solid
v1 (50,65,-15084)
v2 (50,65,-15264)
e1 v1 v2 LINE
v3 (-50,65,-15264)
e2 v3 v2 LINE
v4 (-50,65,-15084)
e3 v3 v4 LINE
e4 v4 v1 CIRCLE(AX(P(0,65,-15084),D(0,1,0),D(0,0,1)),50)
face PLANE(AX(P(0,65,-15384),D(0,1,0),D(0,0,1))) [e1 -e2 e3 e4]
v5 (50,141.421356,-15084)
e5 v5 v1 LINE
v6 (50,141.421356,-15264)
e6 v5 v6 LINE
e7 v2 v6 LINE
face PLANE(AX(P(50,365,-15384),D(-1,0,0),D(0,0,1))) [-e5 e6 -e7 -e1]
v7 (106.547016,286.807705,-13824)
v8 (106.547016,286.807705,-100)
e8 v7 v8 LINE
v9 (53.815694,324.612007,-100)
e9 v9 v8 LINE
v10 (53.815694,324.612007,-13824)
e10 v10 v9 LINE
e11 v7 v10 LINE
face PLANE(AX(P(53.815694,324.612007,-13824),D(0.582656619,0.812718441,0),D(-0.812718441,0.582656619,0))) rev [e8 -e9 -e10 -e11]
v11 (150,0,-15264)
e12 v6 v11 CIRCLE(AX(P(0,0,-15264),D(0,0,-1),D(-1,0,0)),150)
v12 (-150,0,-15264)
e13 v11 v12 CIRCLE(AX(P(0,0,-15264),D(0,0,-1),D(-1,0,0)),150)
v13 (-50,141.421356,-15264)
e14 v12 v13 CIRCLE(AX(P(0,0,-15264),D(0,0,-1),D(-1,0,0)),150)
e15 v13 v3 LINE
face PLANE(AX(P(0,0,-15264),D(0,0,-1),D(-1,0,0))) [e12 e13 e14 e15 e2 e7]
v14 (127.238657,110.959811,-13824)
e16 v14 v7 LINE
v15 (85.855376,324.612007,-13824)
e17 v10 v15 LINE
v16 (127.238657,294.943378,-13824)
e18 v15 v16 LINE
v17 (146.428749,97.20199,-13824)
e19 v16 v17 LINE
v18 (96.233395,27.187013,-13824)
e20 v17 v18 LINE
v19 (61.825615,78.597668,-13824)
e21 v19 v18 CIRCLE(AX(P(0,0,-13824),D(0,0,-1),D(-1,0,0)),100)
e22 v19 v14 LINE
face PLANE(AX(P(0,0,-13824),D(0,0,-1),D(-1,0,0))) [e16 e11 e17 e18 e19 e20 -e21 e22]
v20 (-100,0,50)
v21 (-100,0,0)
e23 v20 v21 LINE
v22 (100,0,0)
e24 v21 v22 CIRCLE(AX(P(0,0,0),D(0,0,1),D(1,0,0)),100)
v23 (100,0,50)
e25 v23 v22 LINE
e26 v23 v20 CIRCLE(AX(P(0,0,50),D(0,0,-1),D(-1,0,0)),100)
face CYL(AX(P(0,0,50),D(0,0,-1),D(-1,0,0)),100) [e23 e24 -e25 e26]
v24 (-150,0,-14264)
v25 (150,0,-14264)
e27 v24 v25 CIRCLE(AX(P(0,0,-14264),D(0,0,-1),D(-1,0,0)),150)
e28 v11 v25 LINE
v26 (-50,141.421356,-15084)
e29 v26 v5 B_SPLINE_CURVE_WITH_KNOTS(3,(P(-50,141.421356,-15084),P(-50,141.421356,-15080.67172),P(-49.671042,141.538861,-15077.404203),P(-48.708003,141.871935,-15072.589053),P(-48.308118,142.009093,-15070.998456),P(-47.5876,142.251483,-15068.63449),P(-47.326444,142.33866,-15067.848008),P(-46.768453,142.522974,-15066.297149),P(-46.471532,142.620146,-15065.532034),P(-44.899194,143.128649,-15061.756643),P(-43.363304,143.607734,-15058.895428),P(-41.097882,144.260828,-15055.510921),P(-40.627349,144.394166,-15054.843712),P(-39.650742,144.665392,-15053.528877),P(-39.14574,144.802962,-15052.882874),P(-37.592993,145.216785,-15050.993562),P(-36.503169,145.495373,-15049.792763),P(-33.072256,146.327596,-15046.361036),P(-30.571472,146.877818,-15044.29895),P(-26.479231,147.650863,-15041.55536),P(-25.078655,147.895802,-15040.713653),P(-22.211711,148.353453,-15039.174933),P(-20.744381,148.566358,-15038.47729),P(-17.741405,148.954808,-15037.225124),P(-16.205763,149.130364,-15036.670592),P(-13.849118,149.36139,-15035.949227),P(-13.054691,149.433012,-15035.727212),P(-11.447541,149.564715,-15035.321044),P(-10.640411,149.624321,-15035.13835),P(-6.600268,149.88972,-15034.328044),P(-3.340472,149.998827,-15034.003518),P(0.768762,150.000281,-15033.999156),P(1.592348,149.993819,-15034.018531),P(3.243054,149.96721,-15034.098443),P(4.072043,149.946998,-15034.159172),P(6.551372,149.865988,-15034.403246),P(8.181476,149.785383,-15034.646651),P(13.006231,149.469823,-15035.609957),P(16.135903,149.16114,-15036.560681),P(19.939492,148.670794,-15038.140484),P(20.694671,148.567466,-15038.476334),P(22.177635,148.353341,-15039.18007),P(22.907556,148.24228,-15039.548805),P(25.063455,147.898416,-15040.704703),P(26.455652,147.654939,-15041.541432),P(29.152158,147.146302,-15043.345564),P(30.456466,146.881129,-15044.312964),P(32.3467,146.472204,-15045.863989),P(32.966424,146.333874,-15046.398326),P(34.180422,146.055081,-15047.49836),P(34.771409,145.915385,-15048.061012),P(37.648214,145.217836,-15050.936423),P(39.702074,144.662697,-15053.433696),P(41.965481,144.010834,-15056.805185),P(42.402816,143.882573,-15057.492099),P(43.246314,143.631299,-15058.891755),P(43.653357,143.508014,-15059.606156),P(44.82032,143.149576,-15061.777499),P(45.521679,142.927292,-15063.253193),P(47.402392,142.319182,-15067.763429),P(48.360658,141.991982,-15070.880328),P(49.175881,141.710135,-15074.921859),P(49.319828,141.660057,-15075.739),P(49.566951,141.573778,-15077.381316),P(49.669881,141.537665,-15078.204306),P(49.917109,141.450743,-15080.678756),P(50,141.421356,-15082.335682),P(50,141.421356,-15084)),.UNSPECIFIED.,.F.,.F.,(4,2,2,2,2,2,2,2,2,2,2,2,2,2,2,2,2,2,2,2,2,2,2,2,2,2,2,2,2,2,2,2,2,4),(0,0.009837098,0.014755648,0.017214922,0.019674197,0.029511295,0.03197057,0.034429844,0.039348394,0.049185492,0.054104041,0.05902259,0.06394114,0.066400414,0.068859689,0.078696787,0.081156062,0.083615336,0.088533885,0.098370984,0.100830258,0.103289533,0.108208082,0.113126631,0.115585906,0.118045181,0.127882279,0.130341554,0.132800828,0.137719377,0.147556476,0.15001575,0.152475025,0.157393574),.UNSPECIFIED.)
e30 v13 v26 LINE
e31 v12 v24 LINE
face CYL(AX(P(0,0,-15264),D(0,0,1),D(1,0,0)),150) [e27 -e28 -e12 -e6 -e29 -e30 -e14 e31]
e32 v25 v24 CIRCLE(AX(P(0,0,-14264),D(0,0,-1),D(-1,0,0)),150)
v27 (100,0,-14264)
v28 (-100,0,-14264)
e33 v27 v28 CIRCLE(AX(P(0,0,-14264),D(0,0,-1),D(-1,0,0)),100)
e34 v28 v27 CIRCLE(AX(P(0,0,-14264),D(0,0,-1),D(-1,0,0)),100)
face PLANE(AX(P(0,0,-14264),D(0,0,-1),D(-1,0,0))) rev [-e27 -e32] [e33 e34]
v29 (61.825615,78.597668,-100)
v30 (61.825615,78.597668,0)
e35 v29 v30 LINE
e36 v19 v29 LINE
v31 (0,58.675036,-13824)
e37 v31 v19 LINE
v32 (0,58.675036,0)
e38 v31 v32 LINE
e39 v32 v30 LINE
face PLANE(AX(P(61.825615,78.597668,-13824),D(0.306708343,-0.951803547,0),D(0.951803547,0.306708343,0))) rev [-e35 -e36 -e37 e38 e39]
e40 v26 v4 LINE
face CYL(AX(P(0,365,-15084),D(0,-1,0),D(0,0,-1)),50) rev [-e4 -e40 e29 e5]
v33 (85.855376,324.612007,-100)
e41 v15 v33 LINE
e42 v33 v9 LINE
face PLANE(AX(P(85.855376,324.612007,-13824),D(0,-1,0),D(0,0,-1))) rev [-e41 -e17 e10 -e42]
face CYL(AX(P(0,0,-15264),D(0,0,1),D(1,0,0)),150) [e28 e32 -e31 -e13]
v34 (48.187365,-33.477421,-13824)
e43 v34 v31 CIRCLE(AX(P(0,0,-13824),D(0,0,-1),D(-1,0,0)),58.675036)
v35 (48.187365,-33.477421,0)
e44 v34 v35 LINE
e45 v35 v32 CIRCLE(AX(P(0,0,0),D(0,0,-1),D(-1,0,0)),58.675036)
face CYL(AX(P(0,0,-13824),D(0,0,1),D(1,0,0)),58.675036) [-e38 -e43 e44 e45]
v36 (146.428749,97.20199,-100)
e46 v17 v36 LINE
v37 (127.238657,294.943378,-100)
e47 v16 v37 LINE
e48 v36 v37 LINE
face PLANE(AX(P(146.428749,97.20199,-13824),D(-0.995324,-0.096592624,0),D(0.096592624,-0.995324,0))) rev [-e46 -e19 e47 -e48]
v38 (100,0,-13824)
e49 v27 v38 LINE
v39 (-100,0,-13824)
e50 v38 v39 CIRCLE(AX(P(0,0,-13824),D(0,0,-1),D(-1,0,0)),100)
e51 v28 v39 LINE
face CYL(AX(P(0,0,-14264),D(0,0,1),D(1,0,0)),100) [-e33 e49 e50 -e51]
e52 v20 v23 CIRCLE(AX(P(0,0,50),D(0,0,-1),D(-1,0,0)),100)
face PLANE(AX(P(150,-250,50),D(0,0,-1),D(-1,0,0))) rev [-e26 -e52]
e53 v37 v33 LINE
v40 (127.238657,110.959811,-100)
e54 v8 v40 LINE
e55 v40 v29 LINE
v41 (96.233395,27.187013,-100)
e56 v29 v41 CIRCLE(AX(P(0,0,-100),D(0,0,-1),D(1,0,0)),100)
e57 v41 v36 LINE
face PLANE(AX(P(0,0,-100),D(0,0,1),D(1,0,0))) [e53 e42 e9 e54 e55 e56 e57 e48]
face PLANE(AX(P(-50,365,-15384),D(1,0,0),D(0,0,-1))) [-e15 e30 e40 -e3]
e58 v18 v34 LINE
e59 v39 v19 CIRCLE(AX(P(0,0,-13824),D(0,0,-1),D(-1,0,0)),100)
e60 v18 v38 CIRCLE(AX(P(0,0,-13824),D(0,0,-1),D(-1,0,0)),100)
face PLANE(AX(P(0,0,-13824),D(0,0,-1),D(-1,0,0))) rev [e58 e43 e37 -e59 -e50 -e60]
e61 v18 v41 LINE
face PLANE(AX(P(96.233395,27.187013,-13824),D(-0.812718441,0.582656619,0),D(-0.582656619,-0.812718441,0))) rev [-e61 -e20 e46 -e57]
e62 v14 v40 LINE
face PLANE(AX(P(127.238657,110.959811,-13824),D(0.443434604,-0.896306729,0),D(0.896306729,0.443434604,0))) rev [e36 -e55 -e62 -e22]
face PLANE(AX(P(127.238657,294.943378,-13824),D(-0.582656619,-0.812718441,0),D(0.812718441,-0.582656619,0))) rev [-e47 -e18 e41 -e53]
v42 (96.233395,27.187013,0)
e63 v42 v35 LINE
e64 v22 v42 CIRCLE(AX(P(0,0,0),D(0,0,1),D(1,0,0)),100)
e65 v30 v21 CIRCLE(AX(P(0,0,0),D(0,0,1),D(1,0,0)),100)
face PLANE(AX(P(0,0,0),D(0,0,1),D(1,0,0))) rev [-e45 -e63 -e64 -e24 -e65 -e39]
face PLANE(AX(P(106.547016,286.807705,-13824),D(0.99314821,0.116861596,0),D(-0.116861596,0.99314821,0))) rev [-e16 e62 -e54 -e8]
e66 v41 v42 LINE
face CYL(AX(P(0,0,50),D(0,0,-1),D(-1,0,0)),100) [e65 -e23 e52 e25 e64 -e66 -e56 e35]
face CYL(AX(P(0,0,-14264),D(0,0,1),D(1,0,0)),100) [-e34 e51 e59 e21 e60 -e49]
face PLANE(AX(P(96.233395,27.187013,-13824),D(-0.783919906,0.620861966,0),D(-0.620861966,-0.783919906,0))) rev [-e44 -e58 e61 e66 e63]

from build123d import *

# Parameters (mm, degrees)
SKETCH1_R           = 100
BOSS_EXTRUDE1_DEPTH = 50
BOSS_EXTRUDE2_DEPTH = 13824
BOSS_EXTRUDE3_START = 440
SKETCH3_R           = 100
BOSS_EXTRUDE3_DEPTH = 440
CUT_EXTRUDE1_START  = -100
CUT_EXTRUDE1_DEPTH  = 100
SKETCH6_R           = 150
BOSS_EXTRUDE5_DEPTH = 2000
CUT_EXTRUDE2_DEPTH  = 326
BOSS_EXTRUDE6_DEPTH = 75
BOSS_EXTRUDE7_START = 1000
SKETCH9_R           = 150
BOSS_EXTRUDE7_DEPTH = 1000
CUT_EXTRUDE3_START  = 65
CUT_EXTRUDE3_DEPTH  = 300
SKETCH11_W          = 300
SKETCH11_H          = 2000
CUT_EXTRUDE4_DEPTH  = 250


with BuildPart() as part:
    # Sketch1 → Boss-Extrude1 (new body)
    with BuildSketch(Plane.XY):
        Circle(SKETCH1_R)
    extrude(amount=BOSS_EXTRUDE1_DEPTH)

    # Sketch2 → Boss-Extrude2 (add)
    with BuildSketch(Plane(origin=(0, 0, 0), x_dir=(-1, 0, 0), z_dir=(0, 0, -1))):
        with BuildLine():
            Line((-96.233395069, 27.187012957), (-146.428749083, 97.201990132))
            Line((-146.428749083, 97.201990132), (-127.238656611, 294.943377783))
            Line((-127.238656611, 294.943377783), (-85.855376139, 324.612007229))
            Line((-85.855376139, 324.612007229), (-53.815694107, 324.612007229))
            Line((-53.815694107, 324.612007229), (-69.835535123, 313.127013254))
            Line((-69.835535123, 313.127013254), (-106.547016375, 286.807704556))
            Line((-106.547016375, 286.807704556), (-127.238656611, 110.959810588))
            Line((-127.238656611, 110.959810588), (-61.825614615, 78.597667761))
            Line((-61.825614615, 78.597667761), (0, 58.675035722))
            ThreePointArc((0, 58.675035722), (51.995426196, -27.188885075), (-48.18736452, -33.477421012))
            Line((-48.18736452, -33.477421012), (-96.233395069, 27.187012957))
        make_face()
    extrude(amount=BOSS_EXTRUDE2_DEPTH)

    # Sketch3 → Boss-Extrude3 (add)
    with BuildSketch(Plane(origin=(0, 0, -13824), x_dir=(-1, 0, 0), z_dir=(0, 0, -1)).offset(BOSS_EXTRUDE3_START)):
        with Locations(Location((0, 0, 0), (0, 0, 128.188900559))):
            Circle(SKETCH3_R)
    extrude(amount=-BOSS_EXTRUDE3_DEPTH)

    # Sketch4 → Cut-Extrude1 (cut)
    with BuildSketch(Plane.XY.offset(CUT_EXTRUDE1_START)):
        with BuildLine():
            Line((96.233395069, 27.187012957), (146.428749083, 97.201990132))
            Line((146.428749083, 97.201990132), (127.238656611, 294.943377783))
            Line((127.238656611, 294.943377783), (85.855376139, 324.612007229))
            Line((85.855376139, 324.612007229), (53.815694107, 324.612007229))
            Line((53.815694107, 324.612007229), (106.547016375, 286.807704556))
            Line((106.547016375, 286.807704556), (127.238656611, 110.959810588))
            Line((127.238656611, 110.959810588), (61.825614615, 78.597667761))
            ThreePointArc((61.825614615, 78.597667761), (83.104912565, 55.619902082), (96.233395069, 27.187012957))
        make_face()
    extrude(amount=CUT_EXTRUDE1_DEPTH, mode=Mode.SUBTRACT)

    # Sketch6 → Boss-Extrude5 (add)
    with BuildSketch(Plane.XY.offset(50)):
        Circle(SKETCH6_R)
    extrude(amount=BOSS_EXTRUDE5_DEPTH)

    # Sketch7 → Cut-Extrude2 (cut)
    with BuildSketch(Plane(origin=(0, 0, 0), x_dir=(1, 0, 0), z_dir=(0, 1, 0))):
        with BuildLine():
            Line((50, -1600), (50, -1900))
            ThreePointArc((50, -1900), (0, -1950), (-50, -1900))
            Line((-50, -1900), (-50, -1600))
            ThreePointArc((-50, -1600), (0, -1550), (50, -1600))
        make_face()
    extrude(amount=CUT_EXTRUDE2_DEPTH, mode=Mode.SUBTRACT)

    # Sketch8 → Boss-Extrude6 (add)
    with BuildSketch(Plane(origin=(0, 0, 0), x_dir=(1, 0, 0), z_dir=(0, 1, 0))):
        with BuildLine():
            Line((-50, -1600), (-50, -1900))
            ThreePointArc((-50, -1900), (0, -1950), (50, -1900))
            Line((50, -1900), (50, -1600))
            ThreePointArc((50, -1600), (0, -1550), (-50, -1600))
        make_face()
    extrude(amount=BOSS_EXTRUDE6_DEPTH)

    # Sketch9 → Boss-Extrude7 (add)
    with BuildSketch(Plane(origin=(0, 0, -14264), x_dir=(-1, 0, 0), z_dir=(0, 0, -1)).offset(BOSS_EXTRUDE7_START)):
        with Locations(Location((0, 0, 0), (0, 0, 180))):
            Circle(SKETCH9_R)
    extrude(amount=-BOSS_EXTRUDE7_DEPTH)

    # Sketch10 → Cut-Extrude3 (cut)
    with BuildSketch(Plane(origin=(0, 0, 0), x_dir=(1, 0, 0), z_dir=(0, 1, 0)).offset(CUT_EXTRUDE3_START)):
        with BuildLine():
            Line((50, 15384), (50, 15084))
            ThreePointArc((50, 15084), (0, 15034), (-50, 15084))
            Line((-50, 15084), (-50, 15384))
            ThreePointArc((-50, 15384), (0, 15434), (50, 15384))
        make_face()
    extrude(amount=CUT_EXTRUDE3_DEPTH, mode=Mode.SUBTRACT)

    # Sketch11 → Cut-Extrude4 (cut, symmetric)
    with BuildSketch(Plane(origin=(0, 0, 0), x_dir=(1, 0, 0), z_dir=(0, 1, 0))):
        with Locations((0, -1050)):
            Rectangle(SKETCH11_W, SKETCH11_H)
    extrude(amount=CUT_EXTRUDE4_DEPTH, both=True, mode=Mode.SUBTRACT)


solid = part.part
